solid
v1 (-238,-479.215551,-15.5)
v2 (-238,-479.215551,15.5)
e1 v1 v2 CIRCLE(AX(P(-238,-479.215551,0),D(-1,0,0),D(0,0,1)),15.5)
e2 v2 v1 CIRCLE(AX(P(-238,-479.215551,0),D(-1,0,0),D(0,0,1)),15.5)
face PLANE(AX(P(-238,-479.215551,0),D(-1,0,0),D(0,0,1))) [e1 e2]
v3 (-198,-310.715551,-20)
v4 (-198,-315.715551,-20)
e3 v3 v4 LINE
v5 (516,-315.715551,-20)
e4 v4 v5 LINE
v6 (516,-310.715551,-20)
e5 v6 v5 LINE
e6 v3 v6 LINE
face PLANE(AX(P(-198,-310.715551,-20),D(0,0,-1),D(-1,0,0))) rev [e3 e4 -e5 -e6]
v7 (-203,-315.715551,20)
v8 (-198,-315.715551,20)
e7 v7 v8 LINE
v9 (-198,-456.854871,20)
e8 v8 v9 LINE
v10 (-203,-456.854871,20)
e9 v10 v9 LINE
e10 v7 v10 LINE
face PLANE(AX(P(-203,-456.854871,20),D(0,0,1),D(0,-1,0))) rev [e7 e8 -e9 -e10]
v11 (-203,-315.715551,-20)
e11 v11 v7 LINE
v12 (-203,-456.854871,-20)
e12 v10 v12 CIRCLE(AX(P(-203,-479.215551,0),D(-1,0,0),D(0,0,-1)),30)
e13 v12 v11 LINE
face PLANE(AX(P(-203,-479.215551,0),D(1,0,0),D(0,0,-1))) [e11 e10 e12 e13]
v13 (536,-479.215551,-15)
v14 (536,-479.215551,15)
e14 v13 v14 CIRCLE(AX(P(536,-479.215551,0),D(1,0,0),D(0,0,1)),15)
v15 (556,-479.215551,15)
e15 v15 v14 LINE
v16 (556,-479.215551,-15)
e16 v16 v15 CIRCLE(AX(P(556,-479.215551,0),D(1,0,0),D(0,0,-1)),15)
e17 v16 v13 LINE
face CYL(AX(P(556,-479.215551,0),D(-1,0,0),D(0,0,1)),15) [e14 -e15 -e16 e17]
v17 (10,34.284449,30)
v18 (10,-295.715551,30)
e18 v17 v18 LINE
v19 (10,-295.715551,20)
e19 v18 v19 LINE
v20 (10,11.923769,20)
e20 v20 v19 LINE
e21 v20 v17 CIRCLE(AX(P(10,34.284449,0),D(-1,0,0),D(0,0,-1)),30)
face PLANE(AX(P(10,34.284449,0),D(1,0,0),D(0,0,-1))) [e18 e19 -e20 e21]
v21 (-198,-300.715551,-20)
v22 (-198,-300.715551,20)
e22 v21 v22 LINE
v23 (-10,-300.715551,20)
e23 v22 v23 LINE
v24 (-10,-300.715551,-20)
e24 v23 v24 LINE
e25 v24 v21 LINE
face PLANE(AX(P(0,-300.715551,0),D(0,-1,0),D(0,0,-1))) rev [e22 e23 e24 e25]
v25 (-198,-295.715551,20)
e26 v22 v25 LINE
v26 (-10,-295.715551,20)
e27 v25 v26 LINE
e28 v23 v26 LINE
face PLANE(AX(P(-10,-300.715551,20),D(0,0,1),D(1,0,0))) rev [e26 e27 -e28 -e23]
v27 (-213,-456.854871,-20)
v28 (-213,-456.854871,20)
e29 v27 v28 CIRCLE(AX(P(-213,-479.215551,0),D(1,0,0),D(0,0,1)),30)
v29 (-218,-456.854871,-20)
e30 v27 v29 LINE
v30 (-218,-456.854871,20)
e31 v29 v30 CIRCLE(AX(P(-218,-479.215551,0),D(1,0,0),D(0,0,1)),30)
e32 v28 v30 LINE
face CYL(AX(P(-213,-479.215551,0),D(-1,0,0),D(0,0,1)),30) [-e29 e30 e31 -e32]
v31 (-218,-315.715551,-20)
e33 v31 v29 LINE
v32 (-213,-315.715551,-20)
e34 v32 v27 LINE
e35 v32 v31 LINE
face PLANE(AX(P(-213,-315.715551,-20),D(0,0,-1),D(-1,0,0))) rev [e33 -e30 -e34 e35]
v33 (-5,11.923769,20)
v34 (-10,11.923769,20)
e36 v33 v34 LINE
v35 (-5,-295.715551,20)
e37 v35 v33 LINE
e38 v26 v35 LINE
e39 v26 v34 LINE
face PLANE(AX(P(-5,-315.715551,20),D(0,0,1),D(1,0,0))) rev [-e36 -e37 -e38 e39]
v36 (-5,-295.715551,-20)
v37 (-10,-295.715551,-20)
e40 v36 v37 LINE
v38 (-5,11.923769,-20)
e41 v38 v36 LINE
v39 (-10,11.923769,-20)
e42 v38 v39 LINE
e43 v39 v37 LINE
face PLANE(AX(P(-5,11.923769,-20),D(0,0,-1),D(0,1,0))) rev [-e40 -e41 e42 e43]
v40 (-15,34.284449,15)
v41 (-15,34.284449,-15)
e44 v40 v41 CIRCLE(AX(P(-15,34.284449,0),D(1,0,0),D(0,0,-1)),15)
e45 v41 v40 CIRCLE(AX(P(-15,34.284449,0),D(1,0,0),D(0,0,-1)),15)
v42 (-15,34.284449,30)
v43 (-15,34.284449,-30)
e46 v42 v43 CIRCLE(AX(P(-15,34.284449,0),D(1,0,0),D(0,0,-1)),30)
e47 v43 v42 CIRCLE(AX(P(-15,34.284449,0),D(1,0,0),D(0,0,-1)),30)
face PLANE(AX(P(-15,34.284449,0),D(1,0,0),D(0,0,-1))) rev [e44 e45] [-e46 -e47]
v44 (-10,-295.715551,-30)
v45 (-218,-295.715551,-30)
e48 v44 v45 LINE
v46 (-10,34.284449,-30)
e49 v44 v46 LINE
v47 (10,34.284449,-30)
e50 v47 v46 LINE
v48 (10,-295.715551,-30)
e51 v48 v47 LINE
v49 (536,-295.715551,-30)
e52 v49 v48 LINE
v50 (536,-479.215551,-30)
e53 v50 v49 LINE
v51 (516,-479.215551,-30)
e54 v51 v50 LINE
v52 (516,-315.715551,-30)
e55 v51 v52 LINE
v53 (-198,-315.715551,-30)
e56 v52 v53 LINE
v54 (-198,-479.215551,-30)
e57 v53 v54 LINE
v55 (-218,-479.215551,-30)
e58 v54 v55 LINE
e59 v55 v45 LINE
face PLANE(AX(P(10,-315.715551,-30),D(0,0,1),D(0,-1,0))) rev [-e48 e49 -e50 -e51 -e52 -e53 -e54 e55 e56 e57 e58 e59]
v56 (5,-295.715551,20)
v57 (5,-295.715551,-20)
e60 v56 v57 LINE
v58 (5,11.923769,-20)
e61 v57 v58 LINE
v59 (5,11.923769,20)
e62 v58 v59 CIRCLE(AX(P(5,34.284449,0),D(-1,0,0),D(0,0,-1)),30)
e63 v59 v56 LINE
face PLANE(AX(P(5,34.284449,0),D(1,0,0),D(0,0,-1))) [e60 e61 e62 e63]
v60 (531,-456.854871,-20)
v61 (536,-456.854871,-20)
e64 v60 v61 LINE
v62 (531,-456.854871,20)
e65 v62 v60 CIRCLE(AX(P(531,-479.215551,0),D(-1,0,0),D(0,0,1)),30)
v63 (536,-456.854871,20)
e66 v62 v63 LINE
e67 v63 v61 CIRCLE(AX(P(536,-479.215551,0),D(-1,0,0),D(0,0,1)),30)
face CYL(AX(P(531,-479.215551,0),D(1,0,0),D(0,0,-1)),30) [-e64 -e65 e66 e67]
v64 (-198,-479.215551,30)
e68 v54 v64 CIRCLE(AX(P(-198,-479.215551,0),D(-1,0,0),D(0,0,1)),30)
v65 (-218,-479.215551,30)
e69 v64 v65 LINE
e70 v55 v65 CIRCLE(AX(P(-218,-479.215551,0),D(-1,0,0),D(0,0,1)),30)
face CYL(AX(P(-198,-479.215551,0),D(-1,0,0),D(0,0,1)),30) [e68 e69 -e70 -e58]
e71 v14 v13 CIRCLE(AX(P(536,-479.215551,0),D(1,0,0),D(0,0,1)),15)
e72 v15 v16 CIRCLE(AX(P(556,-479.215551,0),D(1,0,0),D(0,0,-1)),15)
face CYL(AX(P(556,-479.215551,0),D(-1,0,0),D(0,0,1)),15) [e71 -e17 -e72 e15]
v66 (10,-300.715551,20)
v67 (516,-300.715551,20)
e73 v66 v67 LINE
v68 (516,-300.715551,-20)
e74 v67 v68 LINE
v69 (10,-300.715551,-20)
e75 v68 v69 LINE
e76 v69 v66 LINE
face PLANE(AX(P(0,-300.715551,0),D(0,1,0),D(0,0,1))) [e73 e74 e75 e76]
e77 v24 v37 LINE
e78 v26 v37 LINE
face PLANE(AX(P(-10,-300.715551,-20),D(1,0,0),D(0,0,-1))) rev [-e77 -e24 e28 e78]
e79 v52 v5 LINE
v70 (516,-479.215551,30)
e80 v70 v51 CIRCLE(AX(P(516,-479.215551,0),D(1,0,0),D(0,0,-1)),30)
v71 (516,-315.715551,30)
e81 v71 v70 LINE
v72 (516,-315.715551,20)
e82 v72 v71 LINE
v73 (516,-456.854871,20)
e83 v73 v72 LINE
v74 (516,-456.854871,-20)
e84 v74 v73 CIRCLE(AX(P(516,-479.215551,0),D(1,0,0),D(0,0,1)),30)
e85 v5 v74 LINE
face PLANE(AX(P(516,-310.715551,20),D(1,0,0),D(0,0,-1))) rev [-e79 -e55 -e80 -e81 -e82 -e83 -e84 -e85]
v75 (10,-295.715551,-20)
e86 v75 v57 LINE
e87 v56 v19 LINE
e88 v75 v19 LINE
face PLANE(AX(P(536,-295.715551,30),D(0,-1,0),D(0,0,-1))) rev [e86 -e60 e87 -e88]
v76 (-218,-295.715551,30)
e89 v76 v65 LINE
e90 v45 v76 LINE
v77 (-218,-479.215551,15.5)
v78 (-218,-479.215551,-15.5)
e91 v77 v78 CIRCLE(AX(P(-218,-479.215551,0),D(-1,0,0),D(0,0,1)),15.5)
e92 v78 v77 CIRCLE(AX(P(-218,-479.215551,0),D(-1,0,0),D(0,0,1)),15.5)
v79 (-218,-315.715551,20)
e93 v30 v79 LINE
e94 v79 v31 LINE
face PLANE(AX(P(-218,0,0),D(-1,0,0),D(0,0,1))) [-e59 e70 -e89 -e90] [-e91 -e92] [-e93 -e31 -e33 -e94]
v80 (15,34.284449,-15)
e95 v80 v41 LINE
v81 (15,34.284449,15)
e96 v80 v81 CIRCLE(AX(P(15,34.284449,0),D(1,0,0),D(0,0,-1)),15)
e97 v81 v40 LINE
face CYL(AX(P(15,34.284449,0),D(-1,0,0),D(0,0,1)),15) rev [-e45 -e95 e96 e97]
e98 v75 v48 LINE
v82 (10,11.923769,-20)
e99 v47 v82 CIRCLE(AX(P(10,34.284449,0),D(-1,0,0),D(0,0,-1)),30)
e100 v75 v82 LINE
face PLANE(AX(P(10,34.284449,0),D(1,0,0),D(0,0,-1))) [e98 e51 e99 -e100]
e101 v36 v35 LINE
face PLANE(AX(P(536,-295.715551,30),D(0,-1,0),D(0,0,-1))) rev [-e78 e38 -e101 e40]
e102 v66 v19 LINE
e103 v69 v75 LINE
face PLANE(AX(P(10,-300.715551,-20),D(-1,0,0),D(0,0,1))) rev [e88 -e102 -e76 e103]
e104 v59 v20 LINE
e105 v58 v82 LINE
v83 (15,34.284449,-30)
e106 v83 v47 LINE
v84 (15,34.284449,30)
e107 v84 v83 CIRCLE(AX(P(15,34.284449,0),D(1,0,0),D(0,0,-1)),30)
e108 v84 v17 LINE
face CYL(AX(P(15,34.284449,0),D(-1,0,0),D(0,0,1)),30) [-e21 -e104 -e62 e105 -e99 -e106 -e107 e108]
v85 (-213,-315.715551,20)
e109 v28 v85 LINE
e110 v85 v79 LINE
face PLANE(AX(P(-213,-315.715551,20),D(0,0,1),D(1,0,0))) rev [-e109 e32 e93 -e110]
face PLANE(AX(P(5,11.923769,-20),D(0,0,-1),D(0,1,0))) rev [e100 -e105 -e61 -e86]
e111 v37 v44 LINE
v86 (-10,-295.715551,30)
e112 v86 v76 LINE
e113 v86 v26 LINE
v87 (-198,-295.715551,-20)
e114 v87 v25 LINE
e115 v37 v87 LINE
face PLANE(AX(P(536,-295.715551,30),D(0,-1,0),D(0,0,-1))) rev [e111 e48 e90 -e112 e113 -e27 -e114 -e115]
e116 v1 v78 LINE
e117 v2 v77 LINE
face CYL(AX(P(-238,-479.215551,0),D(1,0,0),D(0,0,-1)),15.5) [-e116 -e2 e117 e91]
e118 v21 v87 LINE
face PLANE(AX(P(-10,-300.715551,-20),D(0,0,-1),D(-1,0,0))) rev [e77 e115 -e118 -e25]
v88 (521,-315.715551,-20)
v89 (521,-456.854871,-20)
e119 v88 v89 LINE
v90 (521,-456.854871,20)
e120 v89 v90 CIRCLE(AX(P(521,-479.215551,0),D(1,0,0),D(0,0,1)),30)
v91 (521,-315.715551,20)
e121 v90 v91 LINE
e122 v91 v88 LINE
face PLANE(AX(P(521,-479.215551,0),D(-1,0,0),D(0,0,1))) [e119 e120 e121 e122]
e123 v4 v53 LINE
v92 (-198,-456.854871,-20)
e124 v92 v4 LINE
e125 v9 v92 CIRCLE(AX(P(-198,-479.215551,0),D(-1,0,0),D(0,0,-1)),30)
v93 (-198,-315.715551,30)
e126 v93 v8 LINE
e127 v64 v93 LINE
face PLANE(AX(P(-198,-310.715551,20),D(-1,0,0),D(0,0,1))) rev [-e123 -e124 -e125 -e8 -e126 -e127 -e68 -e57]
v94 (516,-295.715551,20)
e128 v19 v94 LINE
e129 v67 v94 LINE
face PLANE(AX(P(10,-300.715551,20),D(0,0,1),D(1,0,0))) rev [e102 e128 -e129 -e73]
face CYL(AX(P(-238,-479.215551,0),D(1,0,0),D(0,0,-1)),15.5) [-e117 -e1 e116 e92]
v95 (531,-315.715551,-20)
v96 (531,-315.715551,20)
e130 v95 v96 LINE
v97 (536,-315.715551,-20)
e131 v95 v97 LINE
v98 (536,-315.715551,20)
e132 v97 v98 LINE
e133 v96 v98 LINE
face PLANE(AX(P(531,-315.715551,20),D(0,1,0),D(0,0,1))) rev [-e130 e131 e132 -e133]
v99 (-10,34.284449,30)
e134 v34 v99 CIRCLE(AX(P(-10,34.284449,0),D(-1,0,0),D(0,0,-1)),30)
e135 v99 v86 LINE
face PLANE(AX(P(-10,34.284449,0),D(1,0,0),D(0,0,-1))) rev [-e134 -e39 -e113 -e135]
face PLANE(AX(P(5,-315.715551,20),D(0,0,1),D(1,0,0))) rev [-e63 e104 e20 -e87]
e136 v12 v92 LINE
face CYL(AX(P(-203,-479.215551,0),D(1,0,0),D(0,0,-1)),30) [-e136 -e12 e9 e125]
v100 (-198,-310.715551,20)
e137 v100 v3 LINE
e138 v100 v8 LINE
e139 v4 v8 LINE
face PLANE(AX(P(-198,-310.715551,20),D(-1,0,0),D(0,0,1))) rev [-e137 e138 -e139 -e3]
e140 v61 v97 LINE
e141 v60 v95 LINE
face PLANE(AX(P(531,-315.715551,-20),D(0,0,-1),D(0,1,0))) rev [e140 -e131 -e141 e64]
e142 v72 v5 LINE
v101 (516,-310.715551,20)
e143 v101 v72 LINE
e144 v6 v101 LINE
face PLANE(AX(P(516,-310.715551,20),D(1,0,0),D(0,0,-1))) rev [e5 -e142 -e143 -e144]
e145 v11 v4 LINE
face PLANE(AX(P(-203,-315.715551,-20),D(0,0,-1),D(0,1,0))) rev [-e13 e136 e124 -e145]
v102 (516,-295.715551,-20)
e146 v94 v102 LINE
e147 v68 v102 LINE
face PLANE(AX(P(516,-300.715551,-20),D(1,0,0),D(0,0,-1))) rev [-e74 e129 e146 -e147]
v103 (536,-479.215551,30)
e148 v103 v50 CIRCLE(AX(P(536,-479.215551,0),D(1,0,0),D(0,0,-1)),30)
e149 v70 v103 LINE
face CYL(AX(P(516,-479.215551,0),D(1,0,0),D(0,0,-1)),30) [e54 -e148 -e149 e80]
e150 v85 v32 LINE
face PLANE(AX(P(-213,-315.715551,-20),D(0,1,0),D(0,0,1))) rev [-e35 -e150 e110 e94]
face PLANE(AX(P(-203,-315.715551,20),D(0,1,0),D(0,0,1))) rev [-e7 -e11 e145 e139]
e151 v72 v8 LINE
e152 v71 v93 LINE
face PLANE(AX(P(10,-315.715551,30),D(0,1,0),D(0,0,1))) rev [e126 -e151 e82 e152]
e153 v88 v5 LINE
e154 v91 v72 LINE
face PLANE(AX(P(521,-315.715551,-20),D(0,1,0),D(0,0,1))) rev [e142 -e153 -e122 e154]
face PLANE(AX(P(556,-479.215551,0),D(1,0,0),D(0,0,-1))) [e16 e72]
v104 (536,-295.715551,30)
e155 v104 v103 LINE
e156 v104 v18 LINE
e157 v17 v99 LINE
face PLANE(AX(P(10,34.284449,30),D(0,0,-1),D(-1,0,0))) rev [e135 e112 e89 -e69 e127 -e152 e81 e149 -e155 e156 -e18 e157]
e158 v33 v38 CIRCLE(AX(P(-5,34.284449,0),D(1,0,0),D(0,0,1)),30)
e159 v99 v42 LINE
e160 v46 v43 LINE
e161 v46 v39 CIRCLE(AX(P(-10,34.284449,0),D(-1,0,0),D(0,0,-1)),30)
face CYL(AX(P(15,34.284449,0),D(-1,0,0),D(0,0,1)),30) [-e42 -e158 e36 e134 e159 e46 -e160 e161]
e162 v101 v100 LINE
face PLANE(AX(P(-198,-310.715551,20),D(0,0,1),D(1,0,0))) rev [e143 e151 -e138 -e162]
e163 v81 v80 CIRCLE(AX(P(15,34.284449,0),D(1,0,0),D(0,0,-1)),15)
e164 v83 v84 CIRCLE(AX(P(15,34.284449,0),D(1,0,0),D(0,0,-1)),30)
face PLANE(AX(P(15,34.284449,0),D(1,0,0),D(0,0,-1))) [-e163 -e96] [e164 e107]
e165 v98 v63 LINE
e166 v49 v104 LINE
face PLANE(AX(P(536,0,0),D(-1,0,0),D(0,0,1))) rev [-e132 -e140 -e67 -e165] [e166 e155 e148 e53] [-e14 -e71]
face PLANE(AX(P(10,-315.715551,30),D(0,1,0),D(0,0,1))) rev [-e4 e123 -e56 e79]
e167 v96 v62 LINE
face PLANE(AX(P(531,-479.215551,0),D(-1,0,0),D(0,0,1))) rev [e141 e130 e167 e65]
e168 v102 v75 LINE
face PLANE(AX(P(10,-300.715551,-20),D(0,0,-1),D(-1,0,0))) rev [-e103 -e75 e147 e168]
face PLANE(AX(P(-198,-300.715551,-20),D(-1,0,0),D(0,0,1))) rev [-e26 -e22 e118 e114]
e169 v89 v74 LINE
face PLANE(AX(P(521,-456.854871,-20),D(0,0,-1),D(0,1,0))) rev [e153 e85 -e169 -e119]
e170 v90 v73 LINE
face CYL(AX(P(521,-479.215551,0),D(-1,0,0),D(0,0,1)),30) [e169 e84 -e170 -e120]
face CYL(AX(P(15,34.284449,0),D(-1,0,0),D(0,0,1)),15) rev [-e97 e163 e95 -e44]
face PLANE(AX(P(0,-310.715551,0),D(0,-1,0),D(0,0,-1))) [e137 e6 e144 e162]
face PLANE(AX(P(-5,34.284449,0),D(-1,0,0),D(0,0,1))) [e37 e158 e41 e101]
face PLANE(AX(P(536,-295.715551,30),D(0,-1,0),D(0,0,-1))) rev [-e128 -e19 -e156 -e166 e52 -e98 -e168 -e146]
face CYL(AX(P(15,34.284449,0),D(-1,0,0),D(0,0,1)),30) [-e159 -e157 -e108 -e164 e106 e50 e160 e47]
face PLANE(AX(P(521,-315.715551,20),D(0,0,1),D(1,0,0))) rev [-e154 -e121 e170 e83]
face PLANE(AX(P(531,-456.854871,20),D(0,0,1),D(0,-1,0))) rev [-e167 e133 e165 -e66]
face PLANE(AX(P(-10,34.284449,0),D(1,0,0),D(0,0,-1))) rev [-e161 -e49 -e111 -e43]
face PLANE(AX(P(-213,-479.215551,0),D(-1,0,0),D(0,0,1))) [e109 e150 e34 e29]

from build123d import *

# Parameters (mm, degrees)
SKETCH_2_R           = 30
SKETCH_2_R_2         = 15
EXTRUDE_1_DEPTH      = 15
EXTRUDE_2_DEPTH      = 10
CUT_EXTRUDE_1_DEPTH  = 5
CUT_EXTRUDE_START    = -5
CUT_EXTRUDE_2_DEPTH  = 5
EXTRUDE_3_DEPTH      = 536
EXTRUDE_3_DEPTH_BACK = 218
SKETCH_6_W           = 60
SKETCH_6_H           = 20
SKETCH_8_W           = 188
SKETCH_8_H           = 40
SKETCH_8_W_2         = 506
CUT_EXTRUDE_3_DEPTH  = 5
SKETCH_9_W           = 714
SKETCH_9_H           = 40
CUT_EXTRUDE_4_DEPTH  = 5
EXTRUDE_4_DEPTH      = 20
EXTRUDE_START        = -20
EXTRUDE_5_DEPTH      = 20
CUT_EXTRUDE_5_DEPTH  = 5
CUT_EXTRUDE_6_DEPTH  = 5
CUT_EXTRUDE_7_DEPTH  = 5
CUT_EXTRUDE_8_DEPTH  = 5
SKETCH_17_R          = 15
EXTRUDE_6_DEPTH      = 20
SKETCH_18_R          = 15.5
EXTRUDE_7_DEPTH      = 20


with BuildPart() as part:
    # 草图2 → 凸台-拉伸1 (new, symmetric)
    with BuildSketch(Plane(origin=(0, 0, 0), x_dir=(0, 0, -1), z_dir=(1, 0, 0))):
        with Locations((0, 34.284448819)):
            Circle(SKETCH_2_R)
        with Locations((0, 34.284448819)):
            Circle(SKETCH_2_R_2, mode=Mode.SUBTRACT)
    extrude(amount=EXTRUDE_1_DEPTH, both=True)

    # 草图3 → 凸台-拉伸2 (add, symmetric)
    with BuildSketch(Plane(origin=(0, 0, 0), x_dir=(0, 0, -1), z_dir=(1, 0, 0))):
        with BuildLine():
            Line((-30, 34.284448819), (-30, -315.715551181))
            Line((-30, -315.715551181), (30, -315.715551181))
            Line((30, -315.715551181), (30, 34.284448819))
            ThreePointArc((30, 34.284448819), (0, 4.284448819), (-30, 34.284448819))
        make_face()
    extrude(amount=EXTRUDE_2_DEPTH, both=True)

    # 草图4 → 切除-拉伸1 (cut)
    with BuildSketch(Plane(origin=(10, 0, 0), x_dir=(0, 0, -1), z_dir=(1, 0, 0))):
        with BuildLine():
            Line((-20, -315.715551181), (-20, 11.923769044))
            ThreePointArc((-20, 11.923769044), (0, 4.284448819), (20, 11.923769044))
            Line((20, 11.923769044), (20, -315.715551181))
            Line((20, -315.715551181), (-20, -315.715551181))
        make_face()
    extrude(amount=-CUT_EXTRUDE_1_DEPTH, mode=Mode.SUBTRACT)

    # 草图5 → 切除-拉伸2 (cut)
    with BuildSketch(Plane.ZY.offset(10).offset(CUT_EXTRUDE_START)):
        with BuildLine():
            Line((-20, 11.923769044), (-20, -315.715551181))
            Line((-20, -315.715551181), (20, -315.715551181))
            Line((20, -315.715551181), (20, 11.923769044))
            ThreePointArc((20, 11.923769044), (0, 4.284448819), (-20, 11.923769044))
        make_face()
    extrude(amount=CUT_EXTRUDE_2_DEPTH, mode=Mode.SUBTRACT)

    # 草图6 → 凸台-拉伸3 (add, two sides: drawn at the far end of the back side and taken through both)
    with BuildSketch(Plane(origin=(0, 0, 0), x_dir=(0, 0, -1), z_dir=(1, 0, 0)).offset(-EXTRUDE_3_DEPTH_BACK)):
        with Locations((0, -305.715551181)):
            Rectangle(SKETCH_6_W, SKETCH_6_H)
    extrude(amount=EXTRUDE_3_DEPTH + EXTRUDE_3_DEPTH_BACK)

    # 草图8 → 切除-拉伸3 (cut)
    with BuildSketch(Plane(origin=(0, -295.715551181, 0), x_dir=(1, 0, 0), z_dir=(0, 1, 0))):
        with Locations((-104, 0)):
            Rectangle(SKETCH_8_W, SKETCH_8_H)
        with Locations((263, 0)):
            Rectangle(SKETCH_8_W_2, SKETCH_8_H)
    extrude(amount=-CUT_EXTRUDE_3_DEPTH, mode=Mode.SUBTRACT)

    # 草图9 → 切除-拉伸4 (cut)
    with BuildSketch(Plane.XZ.offset(315.715551181)):
        with Locations((159, 0)):
            Rectangle(SKETCH_9_W, SKETCH_9_H)
    extrude(amount=-CUT_EXTRUDE_4_DEPTH, mode=Mode.SUBTRACT)

    # 草图11 → 凸台-拉伸4 (add)
    with BuildSketch(Plane(origin=(536, 0, 0), x_dir=(0, 0, -1), z_dir=(1, 0, 0))):
        with BuildLine():
            Line((30, -479.215551181), (30, -315.715551181))
            Line((30, -315.715551181), (-30, -315.715551181))
            Line((-30, -315.715551181), (-30, -479.215551181))
            ThreePointArc((-30, -479.215551181), (0, -509.215551181), (30, -479.215551181))
        make_face()
    extrude(amount=-EXTRUDE_4_DEPTH)

    # 草图12 → 凸台-拉伸5 (add)
    with BuildSketch(Plane.ZY.offset(218).offset(EXTRUDE_START)):
        with BuildLine():
            Line((-30, -315.715551181), (30, -315.715551181))
            Line((30, -315.715551181), (30, -479.215551181))
            ThreePointArc((30, -479.215551181), (0, -509.215551181), (-30, -479.215551181))
            Line((-30, -479.215551181), (-30, -315.715551181))
        make_face()
    extrude(amount=EXTRUDE_5_DEPTH)

    # 草图13 → 切除-拉伸5 (cut)
    with BuildSketch(Plane.ZY.offset(218).offset(CUT_EXTRUDE_START)):
        with BuildLine():
            Line((-20, -315.715551181), (20, -315.715551181))
            Line((20, -315.715551181), (20, -456.854871406))
            ThreePointArc((20, -456.854871406), (0, -449.215551181), (-20, -456.854871406))
            Line((-20, -456.854871406), (-20, -315.715551181))
        make_face()
    extrude(amount=CUT_EXTRUDE_5_DEPTH, mode=Mode.SUBTRACT)

    # 草图14 → 切除-拉伸6 (cut)
    with BuildSketch(Plane(origin=(-198, 0, 0), x_dir=(0, 0, -1), z_dir=(1, 0, 0))):
        with BuildLine():
            Line((-20, -456.854871406), (-20, -315.715551181))
            Line((-20, -315.715551181), (20, -315.715551181))
            Line((20, -315.715551181), (20, -456.854871406))
            ThreePointArc((20, -456.854871406), (0, -449.215551181), (-20, -456.854871406))
        make_face()
    extrude(amount=-CUT_EXTRUDE_6_DEPTH, mode=Mode.SUBTRACT)

    # 草图15 → 切除-拉伸7 (cut)
    with BuildSketch(Plane(origin=(536, 0, 0), x_dir=(0, 0, -1), z_dir=(1, 0, 0))):
        with BuildLine():
            Line((-20, -456.854871406), (-20, -315.715551181))
            Line((-20, -315.715551181), (20, -315.715551181))
            Line((20, -315.715551181), (20, -456.854871406))
            ThreePointArc((20, -456.854871406), (0, -449.215551181), (-20, -456.854871406))
        make_face()
    extrude(amount=-CUT_EXTRUDE_7_DEPTH, mode=Mode.SUBTRACT)

    # 草图16 → 切除-拉伸8 (cut)
    with BuildSketch(Plane.ZY.offset(-516).offset(CUT_EXTRUDE_START)):
        with BuildLine():
            Line((-20, -456.854871406), (-20, -315.715551181))
            Line((-20, -315.715551181), (20, -315.715551181))
            Line((20, -315.715551181), (20, -456.854871406))
            ThreePointArc((20, -456.854871406), (0, -449.215551181), (-20, -456.854871406))
        make_face()
    extrude(amount=CUT_EXTRUDE_8_DEPTH, mode=Mode.SUBTRACT)

    # 草图17 → 凸台-拉伸6 (add)
    with BuildSketch(Plane(origin=(536, 0, 0), x_dir=(0, 0, -1), z_dir=(1, 0, 0))):
        with Locations(Location((0, -479.215551181, 0), (0, 0, 180))):
            Circle(SKETCH_17_R)
    extrude(amount=EXTRUDE_6_DEPTH)

    # 草图18 → 凸台-拉伸7 (add)
    with BuildSketch(Plane.ZY.offset(218)):
        with Locations((0, -479.215551181)):
            Circle(SKETCH_18_R)
    extrude(amount=EXTRUDE_7_DEPTH)


solid = part.part
